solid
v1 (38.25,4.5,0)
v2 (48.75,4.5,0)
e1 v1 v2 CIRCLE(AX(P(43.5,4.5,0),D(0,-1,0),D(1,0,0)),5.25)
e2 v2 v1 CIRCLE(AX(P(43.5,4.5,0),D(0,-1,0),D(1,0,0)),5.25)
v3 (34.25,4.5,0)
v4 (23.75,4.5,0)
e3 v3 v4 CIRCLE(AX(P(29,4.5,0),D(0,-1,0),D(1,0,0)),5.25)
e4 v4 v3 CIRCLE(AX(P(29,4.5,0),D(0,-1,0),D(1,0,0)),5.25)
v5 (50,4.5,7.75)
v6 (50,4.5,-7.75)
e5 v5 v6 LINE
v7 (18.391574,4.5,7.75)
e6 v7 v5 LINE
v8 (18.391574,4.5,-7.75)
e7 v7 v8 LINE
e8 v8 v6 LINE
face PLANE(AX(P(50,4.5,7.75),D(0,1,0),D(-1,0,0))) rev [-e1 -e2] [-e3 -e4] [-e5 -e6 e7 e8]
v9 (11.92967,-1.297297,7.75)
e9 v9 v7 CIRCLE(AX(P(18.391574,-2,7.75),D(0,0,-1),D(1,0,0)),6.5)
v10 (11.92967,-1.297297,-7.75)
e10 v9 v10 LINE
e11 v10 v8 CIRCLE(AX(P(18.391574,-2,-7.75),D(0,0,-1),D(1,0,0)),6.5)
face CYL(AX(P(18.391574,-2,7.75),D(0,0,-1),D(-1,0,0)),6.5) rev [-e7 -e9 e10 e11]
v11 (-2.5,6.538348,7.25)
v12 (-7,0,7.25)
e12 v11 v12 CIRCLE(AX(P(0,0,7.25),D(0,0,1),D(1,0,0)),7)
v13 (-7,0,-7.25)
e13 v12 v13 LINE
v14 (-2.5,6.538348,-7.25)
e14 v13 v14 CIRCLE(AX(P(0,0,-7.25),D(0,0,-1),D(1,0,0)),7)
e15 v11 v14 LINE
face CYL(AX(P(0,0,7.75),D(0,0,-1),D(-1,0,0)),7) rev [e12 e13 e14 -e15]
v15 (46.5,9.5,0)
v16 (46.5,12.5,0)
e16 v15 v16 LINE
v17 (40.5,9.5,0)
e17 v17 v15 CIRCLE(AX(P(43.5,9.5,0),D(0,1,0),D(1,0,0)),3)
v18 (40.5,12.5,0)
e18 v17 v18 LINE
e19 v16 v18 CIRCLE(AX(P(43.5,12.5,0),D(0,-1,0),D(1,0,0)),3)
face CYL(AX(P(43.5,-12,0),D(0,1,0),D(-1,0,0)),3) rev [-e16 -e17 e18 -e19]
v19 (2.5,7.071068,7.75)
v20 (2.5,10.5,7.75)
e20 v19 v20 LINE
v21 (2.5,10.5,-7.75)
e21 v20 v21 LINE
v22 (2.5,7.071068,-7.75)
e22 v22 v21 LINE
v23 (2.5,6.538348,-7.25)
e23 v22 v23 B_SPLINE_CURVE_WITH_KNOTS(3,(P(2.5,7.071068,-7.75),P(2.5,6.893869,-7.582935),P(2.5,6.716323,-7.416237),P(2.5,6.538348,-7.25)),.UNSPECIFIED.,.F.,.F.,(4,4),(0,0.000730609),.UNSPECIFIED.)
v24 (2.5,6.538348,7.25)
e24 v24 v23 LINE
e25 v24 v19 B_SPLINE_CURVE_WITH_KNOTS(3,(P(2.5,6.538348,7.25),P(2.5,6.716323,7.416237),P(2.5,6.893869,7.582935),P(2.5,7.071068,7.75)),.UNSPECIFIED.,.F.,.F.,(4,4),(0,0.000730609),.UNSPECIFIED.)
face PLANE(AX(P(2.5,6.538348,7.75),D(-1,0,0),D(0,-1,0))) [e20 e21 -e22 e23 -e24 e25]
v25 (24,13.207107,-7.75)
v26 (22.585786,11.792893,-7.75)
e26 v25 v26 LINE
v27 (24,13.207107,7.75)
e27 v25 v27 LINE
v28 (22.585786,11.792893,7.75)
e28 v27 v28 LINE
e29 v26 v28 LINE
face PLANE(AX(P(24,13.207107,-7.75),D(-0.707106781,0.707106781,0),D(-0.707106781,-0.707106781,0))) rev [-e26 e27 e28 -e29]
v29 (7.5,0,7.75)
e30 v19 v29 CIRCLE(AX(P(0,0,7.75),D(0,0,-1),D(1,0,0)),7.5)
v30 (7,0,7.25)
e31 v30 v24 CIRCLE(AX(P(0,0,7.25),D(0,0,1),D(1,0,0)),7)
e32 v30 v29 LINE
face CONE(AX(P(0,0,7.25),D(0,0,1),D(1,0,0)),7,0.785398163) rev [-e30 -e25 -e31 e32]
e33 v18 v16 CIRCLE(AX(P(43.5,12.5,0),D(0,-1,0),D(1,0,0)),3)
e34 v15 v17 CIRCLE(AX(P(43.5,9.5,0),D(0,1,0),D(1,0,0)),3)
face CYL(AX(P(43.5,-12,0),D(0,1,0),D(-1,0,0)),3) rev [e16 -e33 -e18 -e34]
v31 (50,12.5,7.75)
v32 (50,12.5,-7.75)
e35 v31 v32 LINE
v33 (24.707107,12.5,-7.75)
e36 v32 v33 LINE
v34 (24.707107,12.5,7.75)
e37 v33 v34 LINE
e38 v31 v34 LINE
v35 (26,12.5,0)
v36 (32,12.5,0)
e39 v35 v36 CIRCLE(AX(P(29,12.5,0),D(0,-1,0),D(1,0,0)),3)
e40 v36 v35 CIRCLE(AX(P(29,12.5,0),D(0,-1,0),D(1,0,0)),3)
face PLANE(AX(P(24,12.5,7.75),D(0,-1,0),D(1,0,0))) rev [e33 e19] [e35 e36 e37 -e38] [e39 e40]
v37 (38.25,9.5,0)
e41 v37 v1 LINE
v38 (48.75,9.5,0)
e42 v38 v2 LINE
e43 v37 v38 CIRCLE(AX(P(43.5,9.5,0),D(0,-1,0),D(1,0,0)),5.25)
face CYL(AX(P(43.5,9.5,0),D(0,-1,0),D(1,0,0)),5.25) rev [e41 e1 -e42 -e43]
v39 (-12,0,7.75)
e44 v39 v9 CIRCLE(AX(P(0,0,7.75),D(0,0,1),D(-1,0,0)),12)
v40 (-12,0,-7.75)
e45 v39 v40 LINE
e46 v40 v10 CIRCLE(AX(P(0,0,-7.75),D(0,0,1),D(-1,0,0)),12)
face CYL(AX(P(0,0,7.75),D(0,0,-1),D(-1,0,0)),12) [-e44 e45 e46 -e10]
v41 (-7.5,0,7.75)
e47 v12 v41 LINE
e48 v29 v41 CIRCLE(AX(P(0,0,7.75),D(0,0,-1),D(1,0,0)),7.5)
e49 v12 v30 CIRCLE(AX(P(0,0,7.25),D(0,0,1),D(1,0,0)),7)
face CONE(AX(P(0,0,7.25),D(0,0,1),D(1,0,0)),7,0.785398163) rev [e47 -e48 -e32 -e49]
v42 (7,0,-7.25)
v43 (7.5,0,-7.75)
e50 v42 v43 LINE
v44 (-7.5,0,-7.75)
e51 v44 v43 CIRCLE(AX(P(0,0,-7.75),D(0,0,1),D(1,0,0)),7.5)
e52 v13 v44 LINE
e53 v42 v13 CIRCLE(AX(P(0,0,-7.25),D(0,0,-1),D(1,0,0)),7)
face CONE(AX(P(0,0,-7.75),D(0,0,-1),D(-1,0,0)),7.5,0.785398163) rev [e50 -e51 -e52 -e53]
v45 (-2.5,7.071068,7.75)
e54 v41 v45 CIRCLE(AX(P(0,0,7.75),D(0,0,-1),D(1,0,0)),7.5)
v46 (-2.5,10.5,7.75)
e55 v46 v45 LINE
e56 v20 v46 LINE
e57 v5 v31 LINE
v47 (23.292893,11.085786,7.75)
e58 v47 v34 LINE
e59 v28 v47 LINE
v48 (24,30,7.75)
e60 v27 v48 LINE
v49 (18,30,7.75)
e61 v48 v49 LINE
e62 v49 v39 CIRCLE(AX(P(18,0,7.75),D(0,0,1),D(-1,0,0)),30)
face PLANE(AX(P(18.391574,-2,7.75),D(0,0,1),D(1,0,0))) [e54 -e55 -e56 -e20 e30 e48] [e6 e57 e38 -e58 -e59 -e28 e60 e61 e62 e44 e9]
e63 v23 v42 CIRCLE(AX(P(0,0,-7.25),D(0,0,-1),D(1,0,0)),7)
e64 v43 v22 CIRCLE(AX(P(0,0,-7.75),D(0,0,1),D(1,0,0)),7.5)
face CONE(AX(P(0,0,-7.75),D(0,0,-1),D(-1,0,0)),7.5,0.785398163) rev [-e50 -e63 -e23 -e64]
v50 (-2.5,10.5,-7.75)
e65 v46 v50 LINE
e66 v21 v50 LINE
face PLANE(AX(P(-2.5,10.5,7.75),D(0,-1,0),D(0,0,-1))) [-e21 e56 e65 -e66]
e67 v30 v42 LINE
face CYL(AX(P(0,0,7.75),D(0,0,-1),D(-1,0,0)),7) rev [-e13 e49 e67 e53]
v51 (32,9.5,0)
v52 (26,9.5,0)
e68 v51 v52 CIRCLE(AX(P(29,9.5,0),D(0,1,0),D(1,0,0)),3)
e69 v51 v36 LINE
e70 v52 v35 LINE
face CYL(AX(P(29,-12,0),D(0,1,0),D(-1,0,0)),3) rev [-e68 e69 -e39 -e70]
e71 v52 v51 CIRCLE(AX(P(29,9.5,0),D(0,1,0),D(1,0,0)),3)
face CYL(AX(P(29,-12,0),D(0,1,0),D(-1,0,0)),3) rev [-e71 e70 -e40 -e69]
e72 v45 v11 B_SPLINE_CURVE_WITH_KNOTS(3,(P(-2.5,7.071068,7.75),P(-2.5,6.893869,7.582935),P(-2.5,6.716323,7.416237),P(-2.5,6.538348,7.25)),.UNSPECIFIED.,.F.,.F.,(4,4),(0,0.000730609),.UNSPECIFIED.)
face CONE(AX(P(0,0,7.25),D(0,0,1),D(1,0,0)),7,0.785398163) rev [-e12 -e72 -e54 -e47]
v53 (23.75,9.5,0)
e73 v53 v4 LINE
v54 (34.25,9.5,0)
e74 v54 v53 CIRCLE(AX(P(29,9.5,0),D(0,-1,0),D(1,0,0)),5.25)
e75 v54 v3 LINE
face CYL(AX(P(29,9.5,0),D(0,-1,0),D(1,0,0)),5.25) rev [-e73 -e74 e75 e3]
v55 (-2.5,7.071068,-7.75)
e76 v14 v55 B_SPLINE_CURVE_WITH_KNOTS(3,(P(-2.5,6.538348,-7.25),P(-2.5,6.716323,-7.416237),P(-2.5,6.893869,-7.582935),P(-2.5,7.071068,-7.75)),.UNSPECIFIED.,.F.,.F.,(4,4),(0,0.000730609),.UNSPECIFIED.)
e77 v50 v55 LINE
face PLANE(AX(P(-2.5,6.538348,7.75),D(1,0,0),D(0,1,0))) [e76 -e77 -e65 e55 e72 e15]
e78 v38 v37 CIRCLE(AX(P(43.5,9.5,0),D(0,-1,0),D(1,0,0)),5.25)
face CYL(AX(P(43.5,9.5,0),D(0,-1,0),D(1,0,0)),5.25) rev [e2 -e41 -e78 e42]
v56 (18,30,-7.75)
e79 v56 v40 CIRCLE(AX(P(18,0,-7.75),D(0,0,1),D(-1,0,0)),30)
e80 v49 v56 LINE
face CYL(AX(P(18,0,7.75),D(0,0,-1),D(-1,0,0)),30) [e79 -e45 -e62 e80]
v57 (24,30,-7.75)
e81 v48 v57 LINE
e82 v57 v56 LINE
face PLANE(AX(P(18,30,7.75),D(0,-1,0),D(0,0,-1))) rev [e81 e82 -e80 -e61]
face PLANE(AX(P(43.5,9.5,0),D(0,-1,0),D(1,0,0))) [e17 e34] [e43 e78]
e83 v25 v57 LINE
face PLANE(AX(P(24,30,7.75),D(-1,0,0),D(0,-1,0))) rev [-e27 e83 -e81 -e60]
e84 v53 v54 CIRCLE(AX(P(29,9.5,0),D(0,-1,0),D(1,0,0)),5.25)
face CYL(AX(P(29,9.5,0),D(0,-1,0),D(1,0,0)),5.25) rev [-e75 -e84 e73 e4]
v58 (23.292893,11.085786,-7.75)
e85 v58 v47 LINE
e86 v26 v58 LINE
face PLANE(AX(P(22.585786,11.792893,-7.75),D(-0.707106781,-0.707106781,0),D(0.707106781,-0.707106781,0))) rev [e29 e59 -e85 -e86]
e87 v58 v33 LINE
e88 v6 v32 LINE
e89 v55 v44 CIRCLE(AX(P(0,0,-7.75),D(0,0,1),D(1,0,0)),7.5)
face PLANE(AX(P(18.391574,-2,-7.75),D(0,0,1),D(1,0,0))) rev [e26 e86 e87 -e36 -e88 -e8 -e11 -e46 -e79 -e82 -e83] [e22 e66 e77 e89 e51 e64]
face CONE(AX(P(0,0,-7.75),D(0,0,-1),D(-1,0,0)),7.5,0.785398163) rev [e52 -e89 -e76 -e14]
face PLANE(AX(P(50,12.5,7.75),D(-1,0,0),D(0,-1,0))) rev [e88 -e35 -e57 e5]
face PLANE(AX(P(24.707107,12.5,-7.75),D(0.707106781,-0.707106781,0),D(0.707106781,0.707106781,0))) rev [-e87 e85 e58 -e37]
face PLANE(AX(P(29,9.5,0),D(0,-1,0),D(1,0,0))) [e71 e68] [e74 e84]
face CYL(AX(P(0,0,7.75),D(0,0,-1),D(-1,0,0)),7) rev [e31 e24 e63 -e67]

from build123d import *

# Parameters (mm, degrees)
BOSS_EXTRUDE1_DEPTH     = 7.75
CUT_EXTRUDE1_DEPTH      = 57.216656784
CUT_EXTRUDE1_DEPTH_BACK = 57.216656784
SKETCH3_R               = 3
SKETCH4_R               = 5.25
CUT_EXTRUDE2_DEPTH      = 5
CUT_EXTRUDE3_DEPTH      = 61.334484335
CUT_EXTRUDE3_DEPTH_BACK = 61.334484335
CHAMFER2_SIZE           = 0.5


with BuildPart() as part:
    # Sketch2 → Boss-Extrude1 (new, symmetric)
    with BuildSketch(Plane.XY):
        with BuildLine():
            Line((18, 30), (24, 30))
            Line((24, 30), (24, 12.5))
            Line((24, 12.5), (50, 12.5))
            Line((50, 12.5), (50, 4.5))
            Line((50, 4.5), (18.391574158, 4.5))
            ThreePointArc((18.391574158, 4.5), (14.050927176, 2.838262476), (11.929669724, -1.297297297))
            ThreePointArc((11.929669724, -1.297297297), (-0.649601152, -11.982404531), (-12, 0))
            ThreePointArc((-12, 0), (-3.213203436, 21.213203436), (18, 30))
        make_face()
        with BuildLine():
            Line((-2.5, 6.538348415), (-2.5, 10.5))
            Line((-2.5, 10.5), (2.5, 10.5))
            Line((2.5, 10.5), (2.5, 6.538348415))
            ThreePointArc((2.5, 6.538348415), (0, -7), (-2.5, 6.538348415))
        make_face(mode=Mode.SUBTRACT)
    extrude(amount=BOSS_EXTRUDE1_DEPTH, both=True)

    # Sketch3 → Cut-Extrude1 (cut, two sides: drawn at the far end of the back side and taken through both)
    with BuildSketch(Plane(origin=(0, 12.5, 0), x_dir=(1, 0, 0), z_dir=(0, 1, 0)).offset(-CUT_EXTRUDE1_DEPTH_BACK)):
        with Locations(Location((29, 0, 0), (0, 0, 180))):
            Circle(SKETCH3_R)
        with Locations(Location((43.5, 0, 0), (0, 0, 180))):
            Circle(SKETCH3_R)
    extrude(amount=CUT_EXTRUDE1_DEPTH + CUT_EXTRUDE1_DEPTH_BACK, mode=Mode.SUBTRACT)

    # Sketch4 → Cut-Extrude2 (cut)
    with BuildSketch(Plane.XZ.offset(-4.5)):
        with Locations((29, 0)):
            Circle(SKETCH4_R)
        with Locations((43.5, 0)):
            Circle(SKETCH4_R)
    extrude(amount=-CUT_EXTRUDE2_DEPTH, mode=Mode.SUBTRACT)

    # Sketch5 → Cut-Extrude3 (cut, two sides: drawn at the far end of the back side and taken through both)
    with BuildSketch(Plane.XY.offset(7.75).offset(-CUT_EXTRUDE3_DEPTH_BACK)):
        Polygon((24, 13.207106781), (22.585786438, 11.792893219), (23.292893219, 11.085786438), (24.707106781, 12.5), align=None)
    extrude(amount=CUT_EXTRUDE3_DEPTH + CUT_EXTRUDE3_DEPTH_BACK, mode=Mode.SUBTRACT)

    # Chamfer2
    chamfer2_edges = [part.edges().sort_by_distance(p)[0] for p in [
        (0, -7, -7.75),
        (0, -7, 7.75),
    ]]
    chamfer(chamfer2_edges, length=CHAMFER2_SIZE)


solid = part.part
